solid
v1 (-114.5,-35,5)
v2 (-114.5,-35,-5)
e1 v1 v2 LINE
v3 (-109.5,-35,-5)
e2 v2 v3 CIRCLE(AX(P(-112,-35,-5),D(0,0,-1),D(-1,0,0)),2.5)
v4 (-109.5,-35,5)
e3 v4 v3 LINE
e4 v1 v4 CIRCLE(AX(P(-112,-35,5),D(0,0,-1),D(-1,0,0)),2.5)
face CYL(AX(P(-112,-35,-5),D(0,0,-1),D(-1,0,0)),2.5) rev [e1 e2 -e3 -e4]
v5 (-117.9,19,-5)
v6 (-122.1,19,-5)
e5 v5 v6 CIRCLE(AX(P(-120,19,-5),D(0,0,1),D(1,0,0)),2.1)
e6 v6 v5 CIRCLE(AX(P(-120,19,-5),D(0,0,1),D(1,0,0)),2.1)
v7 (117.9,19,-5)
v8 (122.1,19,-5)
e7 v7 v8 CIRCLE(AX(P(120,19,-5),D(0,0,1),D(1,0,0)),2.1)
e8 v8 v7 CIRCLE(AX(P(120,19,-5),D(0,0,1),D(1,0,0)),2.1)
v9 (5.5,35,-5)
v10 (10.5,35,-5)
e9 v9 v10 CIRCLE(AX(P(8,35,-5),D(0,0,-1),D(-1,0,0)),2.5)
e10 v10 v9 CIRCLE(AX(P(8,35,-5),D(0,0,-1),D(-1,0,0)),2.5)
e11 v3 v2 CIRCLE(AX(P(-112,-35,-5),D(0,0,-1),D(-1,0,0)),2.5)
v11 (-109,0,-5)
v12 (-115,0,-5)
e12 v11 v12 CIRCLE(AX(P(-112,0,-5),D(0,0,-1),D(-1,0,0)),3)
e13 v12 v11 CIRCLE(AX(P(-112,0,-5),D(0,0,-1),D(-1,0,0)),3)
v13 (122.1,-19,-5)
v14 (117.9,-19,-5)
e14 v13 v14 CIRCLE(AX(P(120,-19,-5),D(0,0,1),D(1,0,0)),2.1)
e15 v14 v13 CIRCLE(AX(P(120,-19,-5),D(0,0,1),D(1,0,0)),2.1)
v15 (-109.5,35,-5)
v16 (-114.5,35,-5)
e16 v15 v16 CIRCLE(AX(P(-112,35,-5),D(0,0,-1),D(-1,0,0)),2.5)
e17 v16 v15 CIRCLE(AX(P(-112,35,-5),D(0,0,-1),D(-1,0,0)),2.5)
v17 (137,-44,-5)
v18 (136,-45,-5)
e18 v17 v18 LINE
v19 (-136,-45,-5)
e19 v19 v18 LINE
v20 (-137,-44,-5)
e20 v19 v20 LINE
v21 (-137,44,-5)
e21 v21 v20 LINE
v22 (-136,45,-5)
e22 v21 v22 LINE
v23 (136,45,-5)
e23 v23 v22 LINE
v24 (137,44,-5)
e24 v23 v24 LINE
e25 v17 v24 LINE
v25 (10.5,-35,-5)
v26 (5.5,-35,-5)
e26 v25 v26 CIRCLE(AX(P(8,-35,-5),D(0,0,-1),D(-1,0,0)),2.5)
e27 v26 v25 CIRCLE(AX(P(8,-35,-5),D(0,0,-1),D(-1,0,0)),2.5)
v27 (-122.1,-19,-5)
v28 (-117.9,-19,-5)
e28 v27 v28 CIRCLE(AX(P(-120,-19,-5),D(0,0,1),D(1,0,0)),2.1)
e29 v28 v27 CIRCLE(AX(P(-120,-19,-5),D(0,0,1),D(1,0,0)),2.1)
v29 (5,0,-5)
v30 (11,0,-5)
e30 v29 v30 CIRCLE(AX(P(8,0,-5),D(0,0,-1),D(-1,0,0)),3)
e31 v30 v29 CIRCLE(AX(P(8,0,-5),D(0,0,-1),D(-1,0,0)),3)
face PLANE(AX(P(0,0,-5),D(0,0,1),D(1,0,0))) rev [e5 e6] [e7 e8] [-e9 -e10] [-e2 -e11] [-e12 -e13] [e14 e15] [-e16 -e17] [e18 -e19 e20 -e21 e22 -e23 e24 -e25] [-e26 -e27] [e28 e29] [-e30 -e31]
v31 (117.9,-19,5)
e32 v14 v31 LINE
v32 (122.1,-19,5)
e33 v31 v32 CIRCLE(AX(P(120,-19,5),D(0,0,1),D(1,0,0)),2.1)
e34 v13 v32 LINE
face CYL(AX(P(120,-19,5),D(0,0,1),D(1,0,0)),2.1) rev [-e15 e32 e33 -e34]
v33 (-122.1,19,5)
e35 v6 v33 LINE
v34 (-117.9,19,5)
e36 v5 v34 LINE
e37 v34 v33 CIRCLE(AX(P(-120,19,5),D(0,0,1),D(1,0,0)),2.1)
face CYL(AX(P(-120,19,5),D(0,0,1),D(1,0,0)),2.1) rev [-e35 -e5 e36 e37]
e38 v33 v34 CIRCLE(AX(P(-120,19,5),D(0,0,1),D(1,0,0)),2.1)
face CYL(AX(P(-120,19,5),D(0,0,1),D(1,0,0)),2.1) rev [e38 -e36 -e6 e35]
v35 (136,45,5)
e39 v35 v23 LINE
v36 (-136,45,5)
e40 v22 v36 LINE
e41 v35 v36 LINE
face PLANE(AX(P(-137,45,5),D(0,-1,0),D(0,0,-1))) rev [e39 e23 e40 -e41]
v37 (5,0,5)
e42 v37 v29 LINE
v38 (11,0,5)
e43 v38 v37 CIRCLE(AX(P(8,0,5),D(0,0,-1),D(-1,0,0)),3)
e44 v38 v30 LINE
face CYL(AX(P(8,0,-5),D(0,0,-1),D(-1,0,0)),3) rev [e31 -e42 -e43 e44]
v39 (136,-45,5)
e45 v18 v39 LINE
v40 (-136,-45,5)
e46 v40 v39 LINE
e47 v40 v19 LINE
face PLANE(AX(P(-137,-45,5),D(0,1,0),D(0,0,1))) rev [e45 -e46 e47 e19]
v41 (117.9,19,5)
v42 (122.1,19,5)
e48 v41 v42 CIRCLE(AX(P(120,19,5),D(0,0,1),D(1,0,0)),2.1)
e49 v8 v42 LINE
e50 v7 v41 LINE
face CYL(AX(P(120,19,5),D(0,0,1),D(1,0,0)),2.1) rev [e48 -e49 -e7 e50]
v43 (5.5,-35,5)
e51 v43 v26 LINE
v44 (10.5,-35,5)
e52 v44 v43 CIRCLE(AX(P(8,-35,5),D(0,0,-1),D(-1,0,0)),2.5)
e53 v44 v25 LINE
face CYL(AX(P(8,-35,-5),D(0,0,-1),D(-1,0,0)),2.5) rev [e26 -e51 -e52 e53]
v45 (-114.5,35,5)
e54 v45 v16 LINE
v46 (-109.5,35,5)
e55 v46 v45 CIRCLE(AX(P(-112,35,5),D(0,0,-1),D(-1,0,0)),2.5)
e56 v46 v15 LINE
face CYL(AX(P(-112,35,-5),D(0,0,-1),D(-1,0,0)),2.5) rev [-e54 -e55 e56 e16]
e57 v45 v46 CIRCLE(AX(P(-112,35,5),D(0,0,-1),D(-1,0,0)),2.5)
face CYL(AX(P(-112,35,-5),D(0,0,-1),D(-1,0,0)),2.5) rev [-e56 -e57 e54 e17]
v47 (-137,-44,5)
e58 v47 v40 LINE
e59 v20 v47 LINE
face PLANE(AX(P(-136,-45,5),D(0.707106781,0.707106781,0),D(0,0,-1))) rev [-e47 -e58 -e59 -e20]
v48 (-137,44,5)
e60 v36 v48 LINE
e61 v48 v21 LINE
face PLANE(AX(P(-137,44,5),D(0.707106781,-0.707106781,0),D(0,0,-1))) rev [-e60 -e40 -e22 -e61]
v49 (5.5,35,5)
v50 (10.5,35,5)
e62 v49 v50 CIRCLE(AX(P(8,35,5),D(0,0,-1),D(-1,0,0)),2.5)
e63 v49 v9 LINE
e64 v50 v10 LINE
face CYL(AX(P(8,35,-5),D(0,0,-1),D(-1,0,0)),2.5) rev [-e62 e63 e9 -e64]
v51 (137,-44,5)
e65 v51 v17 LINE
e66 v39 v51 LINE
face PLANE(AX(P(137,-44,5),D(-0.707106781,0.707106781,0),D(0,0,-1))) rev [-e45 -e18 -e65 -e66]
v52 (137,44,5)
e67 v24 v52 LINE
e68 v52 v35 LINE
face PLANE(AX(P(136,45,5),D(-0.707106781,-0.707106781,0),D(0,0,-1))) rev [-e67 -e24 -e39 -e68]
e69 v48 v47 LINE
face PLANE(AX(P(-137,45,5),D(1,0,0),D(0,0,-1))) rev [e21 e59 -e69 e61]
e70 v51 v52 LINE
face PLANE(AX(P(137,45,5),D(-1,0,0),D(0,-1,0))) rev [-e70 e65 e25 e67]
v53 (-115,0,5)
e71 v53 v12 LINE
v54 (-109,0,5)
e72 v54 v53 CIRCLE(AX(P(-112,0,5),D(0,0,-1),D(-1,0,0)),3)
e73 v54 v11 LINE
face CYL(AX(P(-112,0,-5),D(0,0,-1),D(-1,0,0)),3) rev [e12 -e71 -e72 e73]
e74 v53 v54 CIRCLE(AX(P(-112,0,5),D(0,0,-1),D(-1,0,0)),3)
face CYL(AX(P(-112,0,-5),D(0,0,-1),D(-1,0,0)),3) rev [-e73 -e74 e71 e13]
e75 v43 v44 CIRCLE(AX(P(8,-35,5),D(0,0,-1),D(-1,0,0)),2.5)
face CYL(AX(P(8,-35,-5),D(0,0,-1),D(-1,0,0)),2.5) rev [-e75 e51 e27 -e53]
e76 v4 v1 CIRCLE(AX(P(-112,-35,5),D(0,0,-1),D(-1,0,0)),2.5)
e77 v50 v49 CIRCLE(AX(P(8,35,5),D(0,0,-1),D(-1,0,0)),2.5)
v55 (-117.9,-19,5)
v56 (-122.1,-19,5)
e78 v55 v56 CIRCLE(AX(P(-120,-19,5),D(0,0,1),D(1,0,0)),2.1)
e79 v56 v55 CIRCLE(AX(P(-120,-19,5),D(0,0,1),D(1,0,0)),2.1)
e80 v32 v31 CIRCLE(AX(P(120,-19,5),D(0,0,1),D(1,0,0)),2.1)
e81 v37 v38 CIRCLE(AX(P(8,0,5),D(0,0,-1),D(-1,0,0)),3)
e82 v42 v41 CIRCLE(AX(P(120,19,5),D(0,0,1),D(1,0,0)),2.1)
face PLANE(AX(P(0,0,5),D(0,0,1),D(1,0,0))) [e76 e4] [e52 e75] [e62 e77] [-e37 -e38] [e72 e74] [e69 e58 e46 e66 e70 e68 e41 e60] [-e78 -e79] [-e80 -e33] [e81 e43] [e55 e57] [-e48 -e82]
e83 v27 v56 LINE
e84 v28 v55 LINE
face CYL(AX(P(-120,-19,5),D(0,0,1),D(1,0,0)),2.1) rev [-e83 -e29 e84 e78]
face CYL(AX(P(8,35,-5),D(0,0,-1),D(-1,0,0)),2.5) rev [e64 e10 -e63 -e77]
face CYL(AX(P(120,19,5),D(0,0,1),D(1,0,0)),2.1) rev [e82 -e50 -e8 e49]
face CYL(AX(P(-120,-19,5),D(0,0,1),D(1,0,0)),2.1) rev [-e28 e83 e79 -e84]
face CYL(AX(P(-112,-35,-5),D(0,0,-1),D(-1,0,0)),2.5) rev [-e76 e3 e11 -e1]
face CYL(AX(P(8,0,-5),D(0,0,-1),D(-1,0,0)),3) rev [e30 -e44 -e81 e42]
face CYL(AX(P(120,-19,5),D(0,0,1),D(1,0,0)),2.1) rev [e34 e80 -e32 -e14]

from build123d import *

# Parameters (mm, degrees)
SKETCH1_W             = 274
SKETCH1_H             = 90
BOSS_EXTRUDE1_DEPTH   = 5
M5_TAPPED_HOLE1_D     = 4.2
M6_TAPPED_HOLE1_D     = 5
F_6_0MM_BLIND_HOLE1_D = 6
CHAMFER1_SIZE         = 1


with BuildPart() as part:
    # Sketch1 → Boss-Extrude1 (new, symmetric)
    with BuildSketch(Plane.XY):
        Rectangle(SKETCH1_W, SKETCH1_H)
    extrude(amount=BOSS_EXTRUDE1_DEPTH, both=True)

    # M5 Tapped Hole1 (through all)
    with Locations(Plane.XY.offset(5)):
        with Locations((-120, 19), (-120, -19), (120, -19), (120, 19)):
            Hole(M5_TAPPED_HOLE1_D / 2)

    # M6 Tapped Hole1 (through all)
    with Locations(Plane(origin=(0, 0, -5), x_dir=(-1, 0, 0), z_dir=(0, 0, -1))):
        with Locations((112, 35), (112, -35), (-8, -35), (-8, 35)):
            Hole(M6_TAPPED_HOLE1_D / 2)

    # Ø6.0mm blind hole1 (through all)
    with Locations(Plane(origin=(0, 0, -5), x_dir=(-1, 0, 0), z_dir=(0, 0, -1))):
        with Locations((112, 0), (-8, 0)):
            Hole(F_6_0MM_BLIND_HOLE1_D / 2)

    # Chamfer1
    chamfer1_edges = [part.edges().sort_by_distance(p)[0] for p in [
        (137, -45, 0),
        (-137, -45, 0),
        (-137, 45, 0),
        (137, 45, 0),
    ]]
    chamfer(chamfer1_edges, length=CHAMFER1_SIZE)


solid = part.part
